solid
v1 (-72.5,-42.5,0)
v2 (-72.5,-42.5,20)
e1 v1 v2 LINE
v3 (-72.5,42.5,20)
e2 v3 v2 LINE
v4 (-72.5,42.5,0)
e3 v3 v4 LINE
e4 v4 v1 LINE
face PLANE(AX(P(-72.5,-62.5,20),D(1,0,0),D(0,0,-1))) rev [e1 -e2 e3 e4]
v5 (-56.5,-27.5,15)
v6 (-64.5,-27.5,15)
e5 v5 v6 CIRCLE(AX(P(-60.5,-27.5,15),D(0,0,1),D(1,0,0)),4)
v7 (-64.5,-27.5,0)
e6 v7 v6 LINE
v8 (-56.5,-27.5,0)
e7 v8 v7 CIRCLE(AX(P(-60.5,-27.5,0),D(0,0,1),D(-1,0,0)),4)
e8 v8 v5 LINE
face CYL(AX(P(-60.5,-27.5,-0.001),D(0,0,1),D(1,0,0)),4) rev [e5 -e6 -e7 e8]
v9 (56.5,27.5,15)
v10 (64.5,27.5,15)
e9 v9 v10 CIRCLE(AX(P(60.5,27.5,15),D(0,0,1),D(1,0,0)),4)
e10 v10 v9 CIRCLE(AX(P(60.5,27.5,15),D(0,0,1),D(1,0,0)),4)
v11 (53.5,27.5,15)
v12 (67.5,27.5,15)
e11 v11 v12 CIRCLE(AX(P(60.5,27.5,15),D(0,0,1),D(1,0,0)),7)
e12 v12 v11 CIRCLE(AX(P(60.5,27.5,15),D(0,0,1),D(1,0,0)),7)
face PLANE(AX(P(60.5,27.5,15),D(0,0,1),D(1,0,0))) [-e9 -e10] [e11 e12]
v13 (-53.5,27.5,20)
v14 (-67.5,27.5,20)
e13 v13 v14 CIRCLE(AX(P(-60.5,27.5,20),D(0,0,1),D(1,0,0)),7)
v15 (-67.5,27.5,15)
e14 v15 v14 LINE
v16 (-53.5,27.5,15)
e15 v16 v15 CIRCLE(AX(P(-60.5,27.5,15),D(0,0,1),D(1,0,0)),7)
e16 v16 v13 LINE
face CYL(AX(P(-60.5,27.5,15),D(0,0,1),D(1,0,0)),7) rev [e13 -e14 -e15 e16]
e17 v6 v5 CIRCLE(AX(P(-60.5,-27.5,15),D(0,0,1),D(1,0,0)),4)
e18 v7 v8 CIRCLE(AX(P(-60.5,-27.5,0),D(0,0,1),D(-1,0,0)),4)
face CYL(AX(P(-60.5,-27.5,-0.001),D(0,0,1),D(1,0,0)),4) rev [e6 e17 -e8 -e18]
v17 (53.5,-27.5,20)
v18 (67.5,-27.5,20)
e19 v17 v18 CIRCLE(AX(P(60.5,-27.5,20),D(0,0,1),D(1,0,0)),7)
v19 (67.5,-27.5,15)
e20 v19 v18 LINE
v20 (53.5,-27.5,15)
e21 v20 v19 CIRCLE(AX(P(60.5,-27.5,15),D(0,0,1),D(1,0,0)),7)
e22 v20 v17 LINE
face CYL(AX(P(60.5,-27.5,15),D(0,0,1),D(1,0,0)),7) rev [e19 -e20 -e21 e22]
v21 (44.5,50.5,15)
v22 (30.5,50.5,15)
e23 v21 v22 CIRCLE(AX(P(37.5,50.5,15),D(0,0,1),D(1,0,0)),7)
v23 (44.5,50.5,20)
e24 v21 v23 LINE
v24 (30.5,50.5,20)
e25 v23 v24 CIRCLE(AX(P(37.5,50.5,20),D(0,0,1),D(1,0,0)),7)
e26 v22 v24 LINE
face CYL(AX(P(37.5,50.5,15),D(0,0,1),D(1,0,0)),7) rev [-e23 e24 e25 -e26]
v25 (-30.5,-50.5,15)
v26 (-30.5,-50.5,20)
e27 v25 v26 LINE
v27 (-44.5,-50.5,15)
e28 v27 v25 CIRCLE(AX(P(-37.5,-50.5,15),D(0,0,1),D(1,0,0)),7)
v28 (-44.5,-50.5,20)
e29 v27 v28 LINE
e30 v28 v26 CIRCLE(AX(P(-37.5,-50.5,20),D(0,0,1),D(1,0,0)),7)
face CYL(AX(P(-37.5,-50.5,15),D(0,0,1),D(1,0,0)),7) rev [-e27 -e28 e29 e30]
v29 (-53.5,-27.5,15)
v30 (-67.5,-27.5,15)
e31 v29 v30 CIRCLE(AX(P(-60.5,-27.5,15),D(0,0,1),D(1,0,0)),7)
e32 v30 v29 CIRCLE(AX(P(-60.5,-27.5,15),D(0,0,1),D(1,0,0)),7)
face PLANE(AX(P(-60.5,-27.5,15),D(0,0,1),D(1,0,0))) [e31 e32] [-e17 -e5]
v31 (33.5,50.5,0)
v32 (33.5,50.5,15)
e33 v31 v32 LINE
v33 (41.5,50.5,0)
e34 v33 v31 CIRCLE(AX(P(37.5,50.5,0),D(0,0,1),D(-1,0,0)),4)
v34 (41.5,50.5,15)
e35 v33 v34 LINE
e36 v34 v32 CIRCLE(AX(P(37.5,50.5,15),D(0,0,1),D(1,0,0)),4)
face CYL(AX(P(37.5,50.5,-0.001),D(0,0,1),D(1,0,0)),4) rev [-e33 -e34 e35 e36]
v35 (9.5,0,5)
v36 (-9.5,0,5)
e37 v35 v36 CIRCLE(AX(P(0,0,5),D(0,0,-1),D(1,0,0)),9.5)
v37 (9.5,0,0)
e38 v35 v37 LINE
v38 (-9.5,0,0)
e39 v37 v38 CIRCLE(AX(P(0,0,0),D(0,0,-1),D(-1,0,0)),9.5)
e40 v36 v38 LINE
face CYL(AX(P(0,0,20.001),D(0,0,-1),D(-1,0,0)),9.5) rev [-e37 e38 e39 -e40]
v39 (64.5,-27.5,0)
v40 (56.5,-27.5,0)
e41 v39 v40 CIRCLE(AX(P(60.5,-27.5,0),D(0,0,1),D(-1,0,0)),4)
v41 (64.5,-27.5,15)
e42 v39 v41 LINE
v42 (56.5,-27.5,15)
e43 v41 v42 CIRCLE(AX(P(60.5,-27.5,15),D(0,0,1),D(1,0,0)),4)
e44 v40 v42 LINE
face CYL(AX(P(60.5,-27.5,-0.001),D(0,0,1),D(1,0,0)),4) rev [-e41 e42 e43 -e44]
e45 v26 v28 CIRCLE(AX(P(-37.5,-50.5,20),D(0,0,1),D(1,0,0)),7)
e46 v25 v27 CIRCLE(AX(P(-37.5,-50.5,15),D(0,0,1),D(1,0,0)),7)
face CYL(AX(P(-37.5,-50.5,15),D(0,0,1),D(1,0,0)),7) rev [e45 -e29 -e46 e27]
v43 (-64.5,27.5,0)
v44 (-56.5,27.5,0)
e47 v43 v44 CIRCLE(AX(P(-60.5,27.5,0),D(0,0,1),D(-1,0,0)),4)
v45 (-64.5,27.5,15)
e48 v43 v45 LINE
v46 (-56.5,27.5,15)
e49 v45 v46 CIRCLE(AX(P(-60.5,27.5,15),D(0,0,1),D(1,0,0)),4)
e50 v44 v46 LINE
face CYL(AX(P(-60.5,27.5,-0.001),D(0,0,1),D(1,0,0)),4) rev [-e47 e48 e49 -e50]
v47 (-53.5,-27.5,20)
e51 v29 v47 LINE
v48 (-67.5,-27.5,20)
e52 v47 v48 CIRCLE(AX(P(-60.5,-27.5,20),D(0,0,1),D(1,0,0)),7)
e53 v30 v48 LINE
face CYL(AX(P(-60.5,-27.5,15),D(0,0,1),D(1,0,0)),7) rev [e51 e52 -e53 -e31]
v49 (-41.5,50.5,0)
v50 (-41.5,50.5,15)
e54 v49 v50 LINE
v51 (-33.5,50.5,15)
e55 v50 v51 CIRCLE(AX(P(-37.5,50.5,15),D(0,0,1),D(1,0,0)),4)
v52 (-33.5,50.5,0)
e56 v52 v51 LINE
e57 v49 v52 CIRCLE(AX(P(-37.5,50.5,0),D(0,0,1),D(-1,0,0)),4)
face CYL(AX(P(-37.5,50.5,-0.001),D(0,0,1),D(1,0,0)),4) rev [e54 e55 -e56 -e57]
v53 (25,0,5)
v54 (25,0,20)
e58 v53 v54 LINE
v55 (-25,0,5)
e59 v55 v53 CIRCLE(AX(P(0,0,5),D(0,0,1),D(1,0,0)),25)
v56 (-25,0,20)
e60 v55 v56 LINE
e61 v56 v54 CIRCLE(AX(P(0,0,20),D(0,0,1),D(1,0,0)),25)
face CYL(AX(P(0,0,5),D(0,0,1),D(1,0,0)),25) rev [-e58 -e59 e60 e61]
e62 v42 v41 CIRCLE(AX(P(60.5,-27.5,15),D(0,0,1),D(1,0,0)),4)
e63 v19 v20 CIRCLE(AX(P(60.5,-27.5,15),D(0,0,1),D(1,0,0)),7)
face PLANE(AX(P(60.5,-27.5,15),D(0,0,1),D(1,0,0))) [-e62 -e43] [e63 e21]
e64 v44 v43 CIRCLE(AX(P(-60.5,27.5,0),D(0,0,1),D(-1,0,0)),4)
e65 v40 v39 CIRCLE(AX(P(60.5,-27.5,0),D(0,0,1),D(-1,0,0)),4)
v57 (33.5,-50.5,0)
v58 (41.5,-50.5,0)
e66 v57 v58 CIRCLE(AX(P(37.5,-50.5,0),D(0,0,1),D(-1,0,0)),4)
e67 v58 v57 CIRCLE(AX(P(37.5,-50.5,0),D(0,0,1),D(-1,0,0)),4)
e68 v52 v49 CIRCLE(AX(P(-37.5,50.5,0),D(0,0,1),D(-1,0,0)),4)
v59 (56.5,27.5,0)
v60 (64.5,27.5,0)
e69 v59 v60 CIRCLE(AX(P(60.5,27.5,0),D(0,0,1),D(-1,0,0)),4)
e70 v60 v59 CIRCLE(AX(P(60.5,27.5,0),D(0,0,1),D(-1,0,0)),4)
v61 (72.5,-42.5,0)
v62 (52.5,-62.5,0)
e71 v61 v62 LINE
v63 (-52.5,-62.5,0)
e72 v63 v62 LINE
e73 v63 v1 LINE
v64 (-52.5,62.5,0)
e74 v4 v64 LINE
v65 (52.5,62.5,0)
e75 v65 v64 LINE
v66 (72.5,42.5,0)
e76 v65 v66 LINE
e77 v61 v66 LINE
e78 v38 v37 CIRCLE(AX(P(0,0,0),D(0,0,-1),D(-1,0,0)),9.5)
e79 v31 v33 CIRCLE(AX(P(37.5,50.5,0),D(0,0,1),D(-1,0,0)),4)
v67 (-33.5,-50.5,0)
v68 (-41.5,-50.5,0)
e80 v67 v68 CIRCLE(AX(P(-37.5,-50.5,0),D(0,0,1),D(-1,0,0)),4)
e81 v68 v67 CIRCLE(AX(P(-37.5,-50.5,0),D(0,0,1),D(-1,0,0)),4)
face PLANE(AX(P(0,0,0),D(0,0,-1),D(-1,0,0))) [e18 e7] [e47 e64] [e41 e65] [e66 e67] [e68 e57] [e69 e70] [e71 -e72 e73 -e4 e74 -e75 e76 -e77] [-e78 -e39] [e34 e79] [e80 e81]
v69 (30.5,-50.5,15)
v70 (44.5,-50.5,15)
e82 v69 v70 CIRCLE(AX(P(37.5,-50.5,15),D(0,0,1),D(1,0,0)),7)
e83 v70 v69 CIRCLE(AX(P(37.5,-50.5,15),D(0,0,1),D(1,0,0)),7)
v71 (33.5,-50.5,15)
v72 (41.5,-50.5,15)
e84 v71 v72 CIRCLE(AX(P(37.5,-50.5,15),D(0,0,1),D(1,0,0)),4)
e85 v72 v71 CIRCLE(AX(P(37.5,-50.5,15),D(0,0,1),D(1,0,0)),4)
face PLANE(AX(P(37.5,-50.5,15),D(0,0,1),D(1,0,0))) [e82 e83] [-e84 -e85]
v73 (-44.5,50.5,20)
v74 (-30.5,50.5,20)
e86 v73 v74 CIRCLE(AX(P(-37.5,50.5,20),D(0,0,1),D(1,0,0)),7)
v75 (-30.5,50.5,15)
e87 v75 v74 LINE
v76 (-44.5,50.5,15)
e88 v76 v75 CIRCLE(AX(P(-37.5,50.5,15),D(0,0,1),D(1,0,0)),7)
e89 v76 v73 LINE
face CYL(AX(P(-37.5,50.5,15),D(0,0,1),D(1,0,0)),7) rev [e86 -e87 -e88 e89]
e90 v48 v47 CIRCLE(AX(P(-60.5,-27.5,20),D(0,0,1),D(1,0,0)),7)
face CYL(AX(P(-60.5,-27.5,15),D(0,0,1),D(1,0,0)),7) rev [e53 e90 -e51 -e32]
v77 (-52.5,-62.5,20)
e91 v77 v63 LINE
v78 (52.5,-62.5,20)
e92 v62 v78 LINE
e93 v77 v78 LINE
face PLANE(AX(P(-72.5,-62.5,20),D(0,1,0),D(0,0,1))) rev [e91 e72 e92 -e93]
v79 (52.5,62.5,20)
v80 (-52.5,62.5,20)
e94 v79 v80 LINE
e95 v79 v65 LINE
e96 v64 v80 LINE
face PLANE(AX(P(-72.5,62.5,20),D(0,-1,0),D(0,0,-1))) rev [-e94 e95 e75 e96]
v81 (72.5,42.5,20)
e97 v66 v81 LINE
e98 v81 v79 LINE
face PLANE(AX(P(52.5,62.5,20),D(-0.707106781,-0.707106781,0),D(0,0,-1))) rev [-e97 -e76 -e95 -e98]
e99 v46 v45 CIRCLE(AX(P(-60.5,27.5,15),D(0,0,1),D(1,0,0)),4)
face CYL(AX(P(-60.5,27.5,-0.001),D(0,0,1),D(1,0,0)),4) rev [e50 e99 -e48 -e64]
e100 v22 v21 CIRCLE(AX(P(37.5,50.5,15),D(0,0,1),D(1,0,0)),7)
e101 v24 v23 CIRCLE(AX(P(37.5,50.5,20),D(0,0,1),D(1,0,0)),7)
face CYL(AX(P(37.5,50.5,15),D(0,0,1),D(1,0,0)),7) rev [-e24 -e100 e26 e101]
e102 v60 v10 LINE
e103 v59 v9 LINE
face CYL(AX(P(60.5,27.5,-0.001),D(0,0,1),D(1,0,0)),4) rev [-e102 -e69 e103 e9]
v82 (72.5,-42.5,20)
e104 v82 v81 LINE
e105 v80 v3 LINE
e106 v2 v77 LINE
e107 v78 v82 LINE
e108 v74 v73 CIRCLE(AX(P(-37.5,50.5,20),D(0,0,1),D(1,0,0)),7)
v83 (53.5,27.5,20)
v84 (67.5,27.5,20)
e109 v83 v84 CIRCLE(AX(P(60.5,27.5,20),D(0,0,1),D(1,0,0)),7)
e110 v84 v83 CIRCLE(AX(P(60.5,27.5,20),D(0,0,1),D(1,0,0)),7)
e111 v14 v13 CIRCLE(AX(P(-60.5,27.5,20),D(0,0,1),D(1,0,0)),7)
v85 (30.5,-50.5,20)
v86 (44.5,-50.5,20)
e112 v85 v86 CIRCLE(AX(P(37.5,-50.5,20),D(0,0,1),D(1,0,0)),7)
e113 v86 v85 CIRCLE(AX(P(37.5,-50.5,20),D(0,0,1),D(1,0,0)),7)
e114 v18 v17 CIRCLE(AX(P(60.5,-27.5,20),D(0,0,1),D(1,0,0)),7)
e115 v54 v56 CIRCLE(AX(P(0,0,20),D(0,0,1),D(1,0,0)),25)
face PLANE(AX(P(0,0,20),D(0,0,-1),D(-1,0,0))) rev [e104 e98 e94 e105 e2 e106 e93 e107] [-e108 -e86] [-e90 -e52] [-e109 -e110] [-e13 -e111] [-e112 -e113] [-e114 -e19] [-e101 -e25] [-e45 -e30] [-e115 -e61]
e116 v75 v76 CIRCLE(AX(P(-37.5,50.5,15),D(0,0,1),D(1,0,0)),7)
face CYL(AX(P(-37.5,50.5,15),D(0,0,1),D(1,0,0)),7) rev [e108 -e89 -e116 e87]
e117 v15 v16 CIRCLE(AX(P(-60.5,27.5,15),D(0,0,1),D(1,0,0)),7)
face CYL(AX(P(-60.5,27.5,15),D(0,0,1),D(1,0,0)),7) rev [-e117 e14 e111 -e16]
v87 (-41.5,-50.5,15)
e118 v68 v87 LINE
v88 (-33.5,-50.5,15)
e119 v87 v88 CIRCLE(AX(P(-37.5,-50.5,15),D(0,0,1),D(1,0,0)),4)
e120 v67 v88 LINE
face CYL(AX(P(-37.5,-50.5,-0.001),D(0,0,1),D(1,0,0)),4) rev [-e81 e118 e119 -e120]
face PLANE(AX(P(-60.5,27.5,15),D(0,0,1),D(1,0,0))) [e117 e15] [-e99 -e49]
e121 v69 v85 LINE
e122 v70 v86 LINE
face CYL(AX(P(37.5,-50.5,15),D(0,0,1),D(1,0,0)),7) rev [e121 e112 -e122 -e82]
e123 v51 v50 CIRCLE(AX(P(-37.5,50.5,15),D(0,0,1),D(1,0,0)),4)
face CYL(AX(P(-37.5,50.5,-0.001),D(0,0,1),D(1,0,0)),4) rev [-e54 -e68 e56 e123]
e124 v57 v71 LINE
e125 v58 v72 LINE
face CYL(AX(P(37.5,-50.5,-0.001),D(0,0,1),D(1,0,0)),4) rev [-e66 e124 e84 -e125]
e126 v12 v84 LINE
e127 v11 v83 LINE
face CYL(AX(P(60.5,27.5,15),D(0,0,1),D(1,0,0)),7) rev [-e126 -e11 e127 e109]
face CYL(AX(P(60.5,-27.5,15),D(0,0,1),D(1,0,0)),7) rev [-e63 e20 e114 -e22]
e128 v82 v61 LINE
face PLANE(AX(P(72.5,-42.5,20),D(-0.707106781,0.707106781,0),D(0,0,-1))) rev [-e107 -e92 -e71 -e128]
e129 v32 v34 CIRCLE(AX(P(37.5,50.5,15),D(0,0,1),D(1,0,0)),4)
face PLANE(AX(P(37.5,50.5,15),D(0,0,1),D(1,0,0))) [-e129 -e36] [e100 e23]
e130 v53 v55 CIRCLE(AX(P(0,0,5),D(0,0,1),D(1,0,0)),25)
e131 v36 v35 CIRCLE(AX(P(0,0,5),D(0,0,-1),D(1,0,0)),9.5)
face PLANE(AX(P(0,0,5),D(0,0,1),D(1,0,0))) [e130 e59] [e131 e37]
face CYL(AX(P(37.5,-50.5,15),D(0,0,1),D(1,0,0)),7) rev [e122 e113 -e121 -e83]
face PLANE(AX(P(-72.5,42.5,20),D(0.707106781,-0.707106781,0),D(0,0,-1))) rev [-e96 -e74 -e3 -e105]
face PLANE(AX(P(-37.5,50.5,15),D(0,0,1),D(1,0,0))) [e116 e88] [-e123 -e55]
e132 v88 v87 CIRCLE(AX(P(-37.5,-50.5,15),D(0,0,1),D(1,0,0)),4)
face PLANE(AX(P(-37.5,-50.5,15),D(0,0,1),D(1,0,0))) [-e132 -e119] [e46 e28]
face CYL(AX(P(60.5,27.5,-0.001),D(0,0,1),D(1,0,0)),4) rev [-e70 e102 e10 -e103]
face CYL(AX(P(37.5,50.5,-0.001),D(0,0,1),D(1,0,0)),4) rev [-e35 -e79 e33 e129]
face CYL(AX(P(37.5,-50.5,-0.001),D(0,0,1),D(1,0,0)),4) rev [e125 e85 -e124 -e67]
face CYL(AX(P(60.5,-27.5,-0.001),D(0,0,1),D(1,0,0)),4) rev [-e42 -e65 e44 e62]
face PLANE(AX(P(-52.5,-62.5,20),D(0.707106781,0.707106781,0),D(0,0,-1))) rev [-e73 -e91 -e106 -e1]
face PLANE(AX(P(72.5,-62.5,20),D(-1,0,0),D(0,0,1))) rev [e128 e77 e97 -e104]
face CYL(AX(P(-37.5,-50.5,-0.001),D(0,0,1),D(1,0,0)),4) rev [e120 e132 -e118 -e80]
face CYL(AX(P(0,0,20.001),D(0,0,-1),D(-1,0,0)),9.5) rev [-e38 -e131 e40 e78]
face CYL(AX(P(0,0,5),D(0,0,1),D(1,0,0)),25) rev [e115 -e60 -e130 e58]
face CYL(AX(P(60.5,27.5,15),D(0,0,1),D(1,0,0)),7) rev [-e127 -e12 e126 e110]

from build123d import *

# Parameters (mm, degrees)
SKETCH_1_W          = 145
SKETCH_1_H          = 125
EXTRUDE_1_DEPTH     = 20
CHAMFER_1_SIZE      = 20
SKETCH_2_R          = 7
CUT_EXTRUDE_1_DEPTH = 5
CUT_EXTRUDE_2_REACH = 98.889
SKETCH_3_R          = 4
CUT_EXTRUDE_5_REACH = 99.788
SKETCH_6_R          = 9.5
SKETCH_7_R          = 25
CUT_EXTRUDE_6_DEPTH = 15


with BuildPart() as part:
    # 草图1 → 凸台-拉伸1 (new body)
    with BuildSketch(Plane.XY):
        Rectangle(SKETCH_1_W, SKETCH_1_H)
    extrude(amount=EXTRUDE_1_DEPTH)

    # 倒角1
    chamfer_1_edges = [part.edges().sort_by_distance(p)[0] for p in [
        (72.5, -62.5, 10),
        (-72.5, -62.5, 10),
        (-72.5, 62.5, 10),
        (72.5, 62.5, 10),
    ]]
    chamfer(chamfer_1_edges, length=CHAMFER_1_SIZE)

    # 草图2 → 切除-拉伸1 (cut)
    with BuildSketch(Plane.XY.offset(20)):
        with Locations((-37.5, 50.5)):
            Circle(SKETCH_2_R)
        with Locations((37.5, 50.5)):
            Circle(SKETCH_2_R)
        with Locations((-60.5, 27.5)):
            Circle(SKETCH_2_R)
        with Locations((-60.5, -27.5)):
            Circle(SKETCH_2_R)
        with Locations((-37.5, -50.5)):
            Circle(SKETCH_2_R)
        with Locations((37.5, -50.5)):
            Circle(SKETCH_2_R)
        with Locations((60.5, 27.5)):
            Circle(SKETCH_2_R)
        with Locations((60.5, -27.5)):
            Circle(SKETCH_2_R)
    extrude(amount=-CUT_EXTRUDE_1_DEPTH, mode=Mode.SUBTRACT)

    # 草图3 → 切除-拉伸2 (cut, up to next)
    with BuildSketch(Plane.XY.offset(15), mode=Mode.PRIVATE) as cut_extrude_2_sk1:
        with Locations((-37.5, 50.5)):
            Circle(SKETCH_3_R)
    cut_extrude_2_tool1 = extrude(cut_extrude_2_sk1.sketch, amount=-CUT_EXTRUDE_2_REACH, mode=Mode.PRIVATE) & part.part
    # 草图3 → 切除-拉伸2 (cut, up to next)
    with BuildSketch(Plane.XY.offset(15), mode=Mode.PRIVATE) as cut_extrude_2_sk2:
        with Locations((-60.5, 27.5)):
            Circle(SKETCH_3_R)
    cut_extrude_2_tool2 = extrude(cut_extrude_2_sk2.sketch, amount=-CUT_EXTRUDE_2_REACH, mode=Mode.PRIVATE) & part.part
    # 草图3 → 切除-拉伸2 (cut, up to next)
    with BuildSketch(Plane.XY.offset(15), mode=Mode.PRIVATE) as cut_extrude_2_sk3:
        with Locations((-60.5, -27.5)):
            Circle(SKETCH_3_R)
    cut_extrude_2_tool3 = extrude(cut_extrude_2_sk3.sketch, amount=-CUT_EXTRUDE_2_REACH, mode=Mode.PRIVATE) & part.part
    # 草图3 → 切除-拉伸2 (cut, up to next)
    with BuildSketch(Plane.XY.offset(15), mode=Mode.PRIVATE) as cut_extrude_2_sk4:
        with Locations((-37.5, -50.5)):
            Circle(SKETCH_3_R)
    cut_extrude_2_tool4 = extrude(cut_extrude_2_sk4.sketch, amount=-CUT_EXTRUDE_2_REACH, mode=Mode.PRIVATE) & part.part
    # 草图3 → 切除-拉伸2 (cut, up to next)
    with BuildSketch(Plane.XY.offset(15), mode=Mode.PRIVATE) as cut_extrude_2_sk5:
        with Locations((37.5, 50.5)):
            Circle(SKETCH_3_R)
    cut_extrude_2_tool5 = extrude(cut_extrude_2_sk5.sketch, amount=-CUT_EXTRUDE_2_REACH, mode=Mode.PRIVATE) & part.part
    # 草图3 → 切除-拉伸2 (cut, up to next)
    with BuildSketch(Plane.XY.offset(15), mode=Mode.PRIVATE) as cut_extrude_2_sk6:
        with Locations((60.5, 27.5)):
            Circle(SKETCH_3_R)
    cut_extrude_2_tool6 = extrude(cut_extrude_2_sk6.sketch, amount=-CUT_EXTRUDE_2_REACH, mode=Mode.PRIVATE) & part.part
    # 草图3 → 切除-拉伸2 (cut, up to next)
    with BuildSketch(Plane.XY.offset(15), mode=Mode.PRIVATE) as cut_extrude_2_sk7:
        with Locations((60.5, -27.5)):
            Circle(SKETCH_3_R)
    cut_extrude_2_tool7 = extrude(cut_extrude_2_sk7.sketch, amount=-CUT_EXTRUDE_2_REACH, mode=Mode.PRIVATE) & part.part
    # 草图3 → 切除-拉伸2 (cut, up to next)
    with BuildSketch(Plane.XY.offset(15), mode=Mode.PRIVATE) as cut_extrude_2_sk8:
        with Locations((37.5, -50.5)):
            Circle(SKETCH_3_R)
    cut_extrude_2_tool8 = extrude(cut_extrude_2_sk8.sketch, amount=-CUT_EXTRUDE_2_REACH, mode=Mode.PRIVATE) & part.part
    add(cut_extrude_2_tool1.solids().sort_by_distance((-37.5, 50.5, 15))[0], mode=Mode.SUBTRACT)
    add(cut_extrude_2_tool2.solids().sort_by_distance((-60.5, 27.5, 15))[0], mode=Mode.SUBTRACT)
    add(cut_extrude_2_tool3.solids().sort_by_distance((-60.5, -27.5, 15))[0], mode=Mode.SUBTRACT)
    add(cut_extrude_2_tool4.solids().sort_by_distance((-37.5, -50.5, 15))[0], mode=Mode.SUBTRACT)
    add(cut_extrude_2_tool5.solids().sort_by_distance((37.5, 50.5, 15))[0], mode=Mode.SUBTRACT)
    add(cut_extrude_2_tool6.solids().sort_by_distance((60.5, 27.5, 15))[0], mode=Mode.SUBTRACT)
    add(cut_extrude_2_tool7.solids().sort_by_distance((60.5, -27.5, 15))[0], mode=Mode.SUBTRACT)
    add(cut_extrude_2_tool8.solids().sort_by_distance((37.5, -50.5, 15))[0], mode=Mode.SUBTRACT)

    # 草图6 → 切除-拉伸5 (cut, up to next)
    with BuildSketch(Plane(origin=(0, 0, 0), x_dir=(-1, 0, 0), z_dir=(0, 0, -1)), mode=Mode.PRIVATE) as cut_extrude_5_sk1:
        Circle(SKETCH_6_R)
    cut_extrude_5_tool1 = extrude(cut_extrude_5_sk1.sketch, amount=-CUT_EXTRUDE_5_REACH, mode=Mode.PRIVATE) & part.part
    add(cut_extrude_5_tool1.solids().sort_by_distance((0, 0, 0))[0], mode=Mode.SUBTRACT)

    # 草图7 → 切除-拉伸6 (cut)
    with BuildSketch(Plane.XY.offset(20)):
        Circle(SKETCH_7_R)
    extrude(amount=-CUT_EXTRUDE_6_DEPTH, mode=Mode.SUBTRACT)


solid = part.part
